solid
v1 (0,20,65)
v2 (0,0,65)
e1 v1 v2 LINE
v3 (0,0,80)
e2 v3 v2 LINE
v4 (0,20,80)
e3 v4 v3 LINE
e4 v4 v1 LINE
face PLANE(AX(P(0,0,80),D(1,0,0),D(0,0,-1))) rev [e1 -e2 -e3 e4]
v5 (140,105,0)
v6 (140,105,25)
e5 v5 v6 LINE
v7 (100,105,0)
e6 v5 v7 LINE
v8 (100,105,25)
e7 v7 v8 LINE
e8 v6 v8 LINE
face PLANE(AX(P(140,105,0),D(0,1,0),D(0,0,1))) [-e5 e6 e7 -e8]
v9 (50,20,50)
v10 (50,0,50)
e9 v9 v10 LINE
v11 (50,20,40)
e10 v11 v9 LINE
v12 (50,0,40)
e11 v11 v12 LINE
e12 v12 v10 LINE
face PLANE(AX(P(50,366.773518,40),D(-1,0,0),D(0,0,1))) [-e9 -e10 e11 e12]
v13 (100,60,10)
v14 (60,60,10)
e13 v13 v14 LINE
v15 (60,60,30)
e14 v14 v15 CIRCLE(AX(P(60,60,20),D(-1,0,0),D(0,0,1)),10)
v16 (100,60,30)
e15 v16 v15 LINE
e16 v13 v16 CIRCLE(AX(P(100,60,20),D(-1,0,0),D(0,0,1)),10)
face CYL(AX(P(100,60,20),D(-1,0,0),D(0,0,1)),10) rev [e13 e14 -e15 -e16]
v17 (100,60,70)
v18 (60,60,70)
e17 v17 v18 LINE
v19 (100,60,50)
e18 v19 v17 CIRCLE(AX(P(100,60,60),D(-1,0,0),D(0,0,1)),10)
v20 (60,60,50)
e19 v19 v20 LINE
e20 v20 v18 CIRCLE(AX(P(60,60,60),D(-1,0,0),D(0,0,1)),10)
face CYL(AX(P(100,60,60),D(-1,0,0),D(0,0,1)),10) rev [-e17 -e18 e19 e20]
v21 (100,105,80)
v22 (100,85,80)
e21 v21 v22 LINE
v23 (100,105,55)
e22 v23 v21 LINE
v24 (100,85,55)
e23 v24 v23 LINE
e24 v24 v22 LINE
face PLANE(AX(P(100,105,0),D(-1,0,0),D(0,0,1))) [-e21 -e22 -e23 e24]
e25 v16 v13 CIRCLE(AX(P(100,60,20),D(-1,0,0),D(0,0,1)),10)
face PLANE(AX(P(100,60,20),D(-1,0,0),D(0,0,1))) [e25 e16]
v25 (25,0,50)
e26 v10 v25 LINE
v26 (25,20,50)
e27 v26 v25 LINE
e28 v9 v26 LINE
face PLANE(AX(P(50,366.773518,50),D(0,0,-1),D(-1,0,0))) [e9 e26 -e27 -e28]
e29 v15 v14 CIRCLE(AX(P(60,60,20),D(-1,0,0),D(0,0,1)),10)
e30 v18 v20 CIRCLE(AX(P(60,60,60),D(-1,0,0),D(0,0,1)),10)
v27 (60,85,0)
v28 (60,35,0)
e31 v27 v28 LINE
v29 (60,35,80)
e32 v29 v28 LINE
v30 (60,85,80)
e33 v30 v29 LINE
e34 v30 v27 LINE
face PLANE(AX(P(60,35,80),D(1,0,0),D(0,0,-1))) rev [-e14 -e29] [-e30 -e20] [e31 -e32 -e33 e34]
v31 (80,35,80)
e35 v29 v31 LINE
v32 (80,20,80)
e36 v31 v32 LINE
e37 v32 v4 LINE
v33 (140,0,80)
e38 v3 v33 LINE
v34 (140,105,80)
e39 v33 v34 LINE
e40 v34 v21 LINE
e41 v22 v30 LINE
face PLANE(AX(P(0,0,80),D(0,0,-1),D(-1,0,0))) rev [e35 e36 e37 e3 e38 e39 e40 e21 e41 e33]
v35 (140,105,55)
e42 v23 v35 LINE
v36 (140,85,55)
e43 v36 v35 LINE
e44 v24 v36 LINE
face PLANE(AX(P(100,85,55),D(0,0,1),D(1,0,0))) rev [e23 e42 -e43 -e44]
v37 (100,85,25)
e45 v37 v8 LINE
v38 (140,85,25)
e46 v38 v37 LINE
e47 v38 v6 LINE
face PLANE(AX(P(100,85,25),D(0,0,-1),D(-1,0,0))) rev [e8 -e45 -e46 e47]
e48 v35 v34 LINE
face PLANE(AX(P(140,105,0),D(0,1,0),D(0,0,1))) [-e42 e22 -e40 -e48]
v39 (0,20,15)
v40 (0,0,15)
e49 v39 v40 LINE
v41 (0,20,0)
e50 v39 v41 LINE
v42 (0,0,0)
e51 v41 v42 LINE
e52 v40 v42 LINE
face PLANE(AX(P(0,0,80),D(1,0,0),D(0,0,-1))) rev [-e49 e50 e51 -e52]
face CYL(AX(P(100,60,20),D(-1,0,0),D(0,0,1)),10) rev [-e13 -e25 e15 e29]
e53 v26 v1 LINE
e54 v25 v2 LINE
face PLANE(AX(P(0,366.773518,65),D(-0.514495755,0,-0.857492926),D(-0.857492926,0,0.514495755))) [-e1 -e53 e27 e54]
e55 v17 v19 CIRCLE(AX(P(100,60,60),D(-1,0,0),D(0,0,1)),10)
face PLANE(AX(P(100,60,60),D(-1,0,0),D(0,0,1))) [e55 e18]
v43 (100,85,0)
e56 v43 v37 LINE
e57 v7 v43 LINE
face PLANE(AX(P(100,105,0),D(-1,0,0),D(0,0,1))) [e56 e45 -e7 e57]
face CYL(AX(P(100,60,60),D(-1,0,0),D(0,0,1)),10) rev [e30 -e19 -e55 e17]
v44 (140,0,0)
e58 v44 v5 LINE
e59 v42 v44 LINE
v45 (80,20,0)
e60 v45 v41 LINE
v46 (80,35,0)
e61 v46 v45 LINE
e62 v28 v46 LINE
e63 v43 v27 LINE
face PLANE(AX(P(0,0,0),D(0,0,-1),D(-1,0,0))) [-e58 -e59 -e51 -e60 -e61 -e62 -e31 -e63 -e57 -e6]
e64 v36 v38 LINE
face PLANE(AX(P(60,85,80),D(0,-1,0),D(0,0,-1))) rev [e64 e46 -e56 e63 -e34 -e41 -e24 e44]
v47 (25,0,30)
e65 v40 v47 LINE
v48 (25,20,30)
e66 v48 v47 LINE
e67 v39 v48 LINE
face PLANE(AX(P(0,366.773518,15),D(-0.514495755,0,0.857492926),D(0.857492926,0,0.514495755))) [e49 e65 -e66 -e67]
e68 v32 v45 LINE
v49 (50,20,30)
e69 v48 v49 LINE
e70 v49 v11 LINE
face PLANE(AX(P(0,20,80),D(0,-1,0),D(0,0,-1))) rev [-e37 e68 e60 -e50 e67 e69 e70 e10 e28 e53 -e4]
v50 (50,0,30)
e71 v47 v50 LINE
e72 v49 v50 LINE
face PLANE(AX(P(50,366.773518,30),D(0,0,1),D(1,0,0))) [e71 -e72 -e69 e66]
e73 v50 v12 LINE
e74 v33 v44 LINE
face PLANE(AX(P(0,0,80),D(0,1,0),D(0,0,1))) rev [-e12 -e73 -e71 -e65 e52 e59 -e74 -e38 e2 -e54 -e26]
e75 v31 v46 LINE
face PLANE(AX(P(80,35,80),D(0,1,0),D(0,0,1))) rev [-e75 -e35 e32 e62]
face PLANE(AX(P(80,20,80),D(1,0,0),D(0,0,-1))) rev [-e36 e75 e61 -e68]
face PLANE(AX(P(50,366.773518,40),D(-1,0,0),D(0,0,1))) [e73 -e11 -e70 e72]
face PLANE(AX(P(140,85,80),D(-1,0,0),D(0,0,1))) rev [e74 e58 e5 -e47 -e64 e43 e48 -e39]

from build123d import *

# Parameters (mm, degrees)
BASE_STEP_BODY_DEPTH        = 80
UPPER_BLOCK_SKETCH_W        = 40
UPPER_BLOCK_SKETCH_H        = 20
UPPER_BLOCK_DEPTH           = 80
CORNER_NOTCH_SKETCH_25X25_W = 40
CORNER_NOTCH_SKETCH_25X25_H = 30
CORNER_NOTCH_25X25_DEPTH    = 20
SIDE_RECESS_DEPTH           = 183.277261336
SIDE_RECESS_DEPTH_BACK      = 20
SLOT_SKETCH_R               = 10
SLOT_CUT_DEPTH              = 40


with BuildPart() as part:
    # Base Step Profile Sketch → Base Step Body (new body)
    with BuildSketch(Plane.XY):
        Polygon((0, 0), (140, 0), (140, 80), (140, 85), (60, 85), (60, 35), (80, 35), (80, 20), (0, 20), align=None)
    extrude(amount=BASE_STEP_BODY_DEPTH)

    # Upper Block Sketch → Upper Block (add)
    with BuildSketch(Plane.XY.offset(80)):
        with Locations((120, 95)):
            Rectangle(UPPER_BLOCK_SKETCH_W, UPPER_BLOCK_SKETCH_H)
    extrude(amount=-UPPER_BLOCK_DEPTH)

    # Corner Notch Sketch 25x25 → Corner Notch 25x25 (cut)
    with BuildSketch(Plane(origin=(0, 105, 0), x_dir=(1, 0, 0), z_dir=(0, 1, 0))):
        with Locations((120, -40)):
            Rectangle(CORNER_NOTCH_SKETCH_25X25_W, CORNER_NOTCH_SKETCH_25X25_H)
    extrude(amount=-CORNER_NOTCH_25X25_DEPTH, mode=Mode.SUBTRACT)

    # Side Recess Sketch → Side Recess (cut, two sides: drawn at the far end of the back side and taken through both)
    with BuildSketch(Plane(origin=(0, 20, 0), x_dir=(1, 0, 0), z_dir=(0, 1, 0)).offset(-SIDE_RECESS_DEPTH_BACK)):
        Polygon((25, -30), (0, -15), (0, -65), (25, -50), (50, -50), (50, -40), (50, -30), align=None)
    extrude(amount=SIDE_RECESS_DEPTH + SIDE_RECESS_DEPTH_BACK, mode=Mode.SUBTRACT)

    # Slot Sketch → Slot Cut (cut)
    with BuildSketch(Plane.ZY.offset(-60)):
        with Locations((20, 60)):
            Circle(SLOT_SKETCH_R)
        with Locations((60, 60)):
            Circle(SLOT_SKETCH_R)
    extrude(amount=-SLOT_CUT_DEPTH, mode=Mode.SUBTRACT)


solid = part.part
